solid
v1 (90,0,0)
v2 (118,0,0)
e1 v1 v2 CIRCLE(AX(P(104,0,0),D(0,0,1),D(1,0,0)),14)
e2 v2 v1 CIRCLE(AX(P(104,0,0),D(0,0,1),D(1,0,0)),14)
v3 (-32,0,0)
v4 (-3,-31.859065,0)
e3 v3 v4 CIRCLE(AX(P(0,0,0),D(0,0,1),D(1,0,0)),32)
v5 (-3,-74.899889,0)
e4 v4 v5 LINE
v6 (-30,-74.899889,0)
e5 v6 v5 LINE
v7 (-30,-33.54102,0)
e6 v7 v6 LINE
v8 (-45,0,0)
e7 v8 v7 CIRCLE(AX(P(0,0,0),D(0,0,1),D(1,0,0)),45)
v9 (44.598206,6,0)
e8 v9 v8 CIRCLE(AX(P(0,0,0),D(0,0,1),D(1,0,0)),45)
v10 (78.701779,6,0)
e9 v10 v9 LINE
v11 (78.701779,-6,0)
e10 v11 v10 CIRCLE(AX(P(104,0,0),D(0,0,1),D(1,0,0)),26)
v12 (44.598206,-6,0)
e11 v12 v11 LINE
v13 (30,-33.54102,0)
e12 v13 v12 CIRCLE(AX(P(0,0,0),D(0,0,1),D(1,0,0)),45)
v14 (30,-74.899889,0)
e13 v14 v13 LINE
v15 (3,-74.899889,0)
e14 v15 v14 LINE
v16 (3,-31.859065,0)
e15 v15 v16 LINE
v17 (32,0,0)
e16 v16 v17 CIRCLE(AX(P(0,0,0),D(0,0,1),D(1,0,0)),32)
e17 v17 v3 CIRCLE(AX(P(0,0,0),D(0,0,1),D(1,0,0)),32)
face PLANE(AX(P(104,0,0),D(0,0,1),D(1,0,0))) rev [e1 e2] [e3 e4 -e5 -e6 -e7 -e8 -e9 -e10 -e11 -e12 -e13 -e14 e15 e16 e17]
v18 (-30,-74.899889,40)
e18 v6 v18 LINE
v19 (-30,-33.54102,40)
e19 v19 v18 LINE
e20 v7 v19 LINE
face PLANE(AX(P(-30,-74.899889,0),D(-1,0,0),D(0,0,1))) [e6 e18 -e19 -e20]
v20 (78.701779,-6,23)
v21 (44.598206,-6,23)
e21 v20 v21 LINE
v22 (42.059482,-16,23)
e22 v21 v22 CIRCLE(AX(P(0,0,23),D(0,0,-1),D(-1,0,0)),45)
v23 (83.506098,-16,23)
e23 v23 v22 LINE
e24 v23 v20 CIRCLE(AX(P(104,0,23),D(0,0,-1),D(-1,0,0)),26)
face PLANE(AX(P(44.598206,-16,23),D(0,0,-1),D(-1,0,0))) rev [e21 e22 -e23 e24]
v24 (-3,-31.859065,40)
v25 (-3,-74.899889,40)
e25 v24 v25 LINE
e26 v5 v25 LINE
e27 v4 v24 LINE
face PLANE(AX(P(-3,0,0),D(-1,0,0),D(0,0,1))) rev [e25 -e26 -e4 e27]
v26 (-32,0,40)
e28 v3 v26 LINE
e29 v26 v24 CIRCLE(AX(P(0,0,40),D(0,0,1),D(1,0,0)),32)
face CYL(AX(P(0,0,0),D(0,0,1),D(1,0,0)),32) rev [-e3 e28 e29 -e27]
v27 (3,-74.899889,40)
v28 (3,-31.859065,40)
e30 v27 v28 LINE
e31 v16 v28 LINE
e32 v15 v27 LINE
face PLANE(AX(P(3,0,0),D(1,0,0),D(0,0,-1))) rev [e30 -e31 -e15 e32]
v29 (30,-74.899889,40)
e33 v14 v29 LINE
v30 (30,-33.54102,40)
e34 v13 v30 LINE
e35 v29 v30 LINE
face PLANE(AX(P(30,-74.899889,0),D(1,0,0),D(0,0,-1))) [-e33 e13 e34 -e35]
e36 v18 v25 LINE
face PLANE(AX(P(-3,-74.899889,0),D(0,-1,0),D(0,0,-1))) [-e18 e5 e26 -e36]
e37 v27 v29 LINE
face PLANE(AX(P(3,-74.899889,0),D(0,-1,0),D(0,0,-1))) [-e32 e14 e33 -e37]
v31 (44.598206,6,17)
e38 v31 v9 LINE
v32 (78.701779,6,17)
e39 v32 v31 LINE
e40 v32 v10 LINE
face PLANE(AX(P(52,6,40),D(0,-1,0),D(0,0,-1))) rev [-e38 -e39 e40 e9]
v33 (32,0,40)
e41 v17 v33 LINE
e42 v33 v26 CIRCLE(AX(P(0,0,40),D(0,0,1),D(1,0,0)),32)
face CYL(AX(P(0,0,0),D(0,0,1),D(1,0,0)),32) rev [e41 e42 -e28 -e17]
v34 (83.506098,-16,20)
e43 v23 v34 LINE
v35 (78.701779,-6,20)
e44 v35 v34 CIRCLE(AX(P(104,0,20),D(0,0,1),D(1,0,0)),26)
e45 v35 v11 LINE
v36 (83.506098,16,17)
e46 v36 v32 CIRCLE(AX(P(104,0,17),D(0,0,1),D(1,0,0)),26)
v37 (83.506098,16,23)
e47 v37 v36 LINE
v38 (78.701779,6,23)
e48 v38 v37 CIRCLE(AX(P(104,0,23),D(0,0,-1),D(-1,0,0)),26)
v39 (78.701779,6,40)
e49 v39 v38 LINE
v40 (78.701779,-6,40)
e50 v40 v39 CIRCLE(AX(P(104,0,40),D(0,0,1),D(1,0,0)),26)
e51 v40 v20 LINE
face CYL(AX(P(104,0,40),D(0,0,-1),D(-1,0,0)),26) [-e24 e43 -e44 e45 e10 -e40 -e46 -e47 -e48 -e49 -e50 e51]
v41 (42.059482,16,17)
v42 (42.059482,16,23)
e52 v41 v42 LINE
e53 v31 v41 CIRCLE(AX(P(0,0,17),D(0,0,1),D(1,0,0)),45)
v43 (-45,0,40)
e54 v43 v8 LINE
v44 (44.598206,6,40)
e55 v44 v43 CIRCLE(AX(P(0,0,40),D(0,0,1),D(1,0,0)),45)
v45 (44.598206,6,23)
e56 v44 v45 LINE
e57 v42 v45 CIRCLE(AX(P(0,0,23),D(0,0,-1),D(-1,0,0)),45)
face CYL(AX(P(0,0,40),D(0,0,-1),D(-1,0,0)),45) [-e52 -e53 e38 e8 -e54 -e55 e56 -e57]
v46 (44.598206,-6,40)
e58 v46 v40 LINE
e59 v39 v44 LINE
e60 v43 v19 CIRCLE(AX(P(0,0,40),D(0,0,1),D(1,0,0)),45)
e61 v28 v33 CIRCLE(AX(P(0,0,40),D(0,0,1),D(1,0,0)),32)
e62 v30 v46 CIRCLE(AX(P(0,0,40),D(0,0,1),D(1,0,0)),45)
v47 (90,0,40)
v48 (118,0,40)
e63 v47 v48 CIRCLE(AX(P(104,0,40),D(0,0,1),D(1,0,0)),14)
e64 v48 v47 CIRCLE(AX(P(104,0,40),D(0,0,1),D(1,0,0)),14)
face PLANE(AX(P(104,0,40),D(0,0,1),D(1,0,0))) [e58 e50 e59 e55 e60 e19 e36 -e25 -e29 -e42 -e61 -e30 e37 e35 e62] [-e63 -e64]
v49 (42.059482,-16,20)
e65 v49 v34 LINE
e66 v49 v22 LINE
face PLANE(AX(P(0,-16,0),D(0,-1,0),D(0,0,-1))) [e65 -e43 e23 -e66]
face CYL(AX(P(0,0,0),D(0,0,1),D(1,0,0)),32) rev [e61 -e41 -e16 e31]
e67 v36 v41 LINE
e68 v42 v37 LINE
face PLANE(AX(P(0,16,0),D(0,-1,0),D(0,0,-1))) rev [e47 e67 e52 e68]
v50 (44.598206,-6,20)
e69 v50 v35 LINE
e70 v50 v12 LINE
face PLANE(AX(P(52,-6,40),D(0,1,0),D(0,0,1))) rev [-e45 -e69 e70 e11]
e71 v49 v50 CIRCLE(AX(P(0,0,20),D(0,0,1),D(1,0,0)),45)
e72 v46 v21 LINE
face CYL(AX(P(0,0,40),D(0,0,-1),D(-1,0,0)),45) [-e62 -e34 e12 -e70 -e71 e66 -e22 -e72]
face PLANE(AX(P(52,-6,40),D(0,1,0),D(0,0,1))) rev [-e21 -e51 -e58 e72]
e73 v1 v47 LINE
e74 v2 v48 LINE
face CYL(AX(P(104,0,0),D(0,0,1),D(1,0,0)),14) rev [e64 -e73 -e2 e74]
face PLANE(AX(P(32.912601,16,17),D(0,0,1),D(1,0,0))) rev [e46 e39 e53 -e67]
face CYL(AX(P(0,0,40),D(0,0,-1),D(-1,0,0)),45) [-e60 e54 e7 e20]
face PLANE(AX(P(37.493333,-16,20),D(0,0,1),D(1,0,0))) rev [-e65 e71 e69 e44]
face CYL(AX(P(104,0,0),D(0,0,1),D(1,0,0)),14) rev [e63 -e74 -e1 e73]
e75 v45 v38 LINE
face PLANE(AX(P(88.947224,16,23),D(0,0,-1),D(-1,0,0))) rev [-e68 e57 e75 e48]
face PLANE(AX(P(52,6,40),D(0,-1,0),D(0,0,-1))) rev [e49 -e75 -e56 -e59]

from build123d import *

# Parameters (mm, degrees)
CLAMP_BODY_DEPTH             = 40
PIN_BORE_SKETCH_R            = 14
PIN_BORE_28_DEPTH            = 40
CLAMP_START                  = -40
CLAMP_BORE_64_AND_SLIT_DEPTH = 40
LEVER_START                  = -40
LEVER_ARM_DEPTH              = 40
ARM_WEB_A_DEPTH              = 10
ARM_WEB_B_DEPTH              = 10


with BuildPart() as part:
    # Clamp Body Sketch → Clamp Body (new body)
    with BuildSketch(Plane.XY):
        with BuildLine():
            Line((52, -6), (78.701778719, -6))
            ThreePointArc((78.701778719, -6), (130, 0), (78.701778719, 6))
            Line((78.701778719, 6), (52, 6))
            Line((52, 6), (44.598206242, 6))
            ThreePointArc((44.598206242, 6), (-45, 0), (44.598206242, -6))
            Line((44.598206242, -6), (52, -6))
        make_face()
    extrude(amount=CLAMP_BODY_DEPTH)

    # Pin Bore Sketch → Pin Bore Ø28 (cut)
    with BuildSketch(Plane.XY.offset(40)):
        with Locations((104, 0)):
            Circle(PIN_BORE_SKETCH_R)
    extrude(amount=-PIN_BORE_28_DEPTH, mode=Mode.SUBTRACT)

    # Clamp Bore and Slit Sketch → Clamp Bore Ø64 and Slit (cut)
    with BuildSketch(Plane.XY.offset(40).offset(CLAMP_START)):
        with BuildLine():
            ThreePointArc((-3, -44.899888641), (0, -45), (3, -44.899888641))
            Line((3, -44.899888641), (3, -31.859064644))
            ThreePointArc((3, -31.859064644), (19.483742845, -25.38471518), (30, -11.135528726))
            ThreePointArc((30, -11.135528726), (0, 32), (-30, -11.135528726))
            ThreePointArc((-30, -11.135528726), (-19.483742845, -25.38471518), (-3, -31.859064644))
            Line((-3, -31.859064644), (-3, -44.899888641))
        make_face()
    extrude(amount=CLAMP_BORE_64_AND_SLIT_DEPTH, mode=Mode.SUBTRACT)

    # Lever Arm Sketch → Lever Arm (add)
    with BuildSketch(Plane.XY.offset(40).offset(LEVER_START)):
        with BuildLine():
            Line((-3, -44.899888641), (-3, -74.899888641))
            Line((-3, -74.899888641), (-30, -74.899888641))
            Line((-30, -74.899888641), (-30, -33.541019662))
            ThreePointArc((-30, -33.541019662), (-17.450099602, -41.478838266), (-3, -44.899888641))
        make_face()
        with BuildLine():
            Line((3, -44.899888641), (3, -74.899888641))
            Line((3, -74.899888641), (30, -74.899888641))
            Line((30, -74.899888641), (30, -33.541019662))
            ThreePointArc((30, -33.541019662), (17.450099602, -41.478838266), (3, -44.899888641))
        make_face()
    extrude(amount=LEVER_ARM_DEPTH)

    # Arm Web A Sketch → Arm Web A (add)
    with BuildSketch(Plane(origin=(0, 6, 0), x_dir=(1, 0, 0), z_dir=(0, 1, 0))):
        Polygon((32.912600582, -20), (32.912600582, -17), (88.947224008, -17), (88.947224008, -23), (32.912600582, -23), align=None)
    extrude(amount=ARM_WEB_A_DEPTH)

    # Arm Web B Sketch → Arm Web B (add)
    with BuildSketch(Plane.XZ.offset(6)):
        Polygon((44.598206242, 23), (37.493332774, 23), (37.493332774, 20), (86.340481081, 20), (86.340481081, 23), align=None)
    extrude(amount=ARM_WEB_B_DEPTH)


solid = part.part
